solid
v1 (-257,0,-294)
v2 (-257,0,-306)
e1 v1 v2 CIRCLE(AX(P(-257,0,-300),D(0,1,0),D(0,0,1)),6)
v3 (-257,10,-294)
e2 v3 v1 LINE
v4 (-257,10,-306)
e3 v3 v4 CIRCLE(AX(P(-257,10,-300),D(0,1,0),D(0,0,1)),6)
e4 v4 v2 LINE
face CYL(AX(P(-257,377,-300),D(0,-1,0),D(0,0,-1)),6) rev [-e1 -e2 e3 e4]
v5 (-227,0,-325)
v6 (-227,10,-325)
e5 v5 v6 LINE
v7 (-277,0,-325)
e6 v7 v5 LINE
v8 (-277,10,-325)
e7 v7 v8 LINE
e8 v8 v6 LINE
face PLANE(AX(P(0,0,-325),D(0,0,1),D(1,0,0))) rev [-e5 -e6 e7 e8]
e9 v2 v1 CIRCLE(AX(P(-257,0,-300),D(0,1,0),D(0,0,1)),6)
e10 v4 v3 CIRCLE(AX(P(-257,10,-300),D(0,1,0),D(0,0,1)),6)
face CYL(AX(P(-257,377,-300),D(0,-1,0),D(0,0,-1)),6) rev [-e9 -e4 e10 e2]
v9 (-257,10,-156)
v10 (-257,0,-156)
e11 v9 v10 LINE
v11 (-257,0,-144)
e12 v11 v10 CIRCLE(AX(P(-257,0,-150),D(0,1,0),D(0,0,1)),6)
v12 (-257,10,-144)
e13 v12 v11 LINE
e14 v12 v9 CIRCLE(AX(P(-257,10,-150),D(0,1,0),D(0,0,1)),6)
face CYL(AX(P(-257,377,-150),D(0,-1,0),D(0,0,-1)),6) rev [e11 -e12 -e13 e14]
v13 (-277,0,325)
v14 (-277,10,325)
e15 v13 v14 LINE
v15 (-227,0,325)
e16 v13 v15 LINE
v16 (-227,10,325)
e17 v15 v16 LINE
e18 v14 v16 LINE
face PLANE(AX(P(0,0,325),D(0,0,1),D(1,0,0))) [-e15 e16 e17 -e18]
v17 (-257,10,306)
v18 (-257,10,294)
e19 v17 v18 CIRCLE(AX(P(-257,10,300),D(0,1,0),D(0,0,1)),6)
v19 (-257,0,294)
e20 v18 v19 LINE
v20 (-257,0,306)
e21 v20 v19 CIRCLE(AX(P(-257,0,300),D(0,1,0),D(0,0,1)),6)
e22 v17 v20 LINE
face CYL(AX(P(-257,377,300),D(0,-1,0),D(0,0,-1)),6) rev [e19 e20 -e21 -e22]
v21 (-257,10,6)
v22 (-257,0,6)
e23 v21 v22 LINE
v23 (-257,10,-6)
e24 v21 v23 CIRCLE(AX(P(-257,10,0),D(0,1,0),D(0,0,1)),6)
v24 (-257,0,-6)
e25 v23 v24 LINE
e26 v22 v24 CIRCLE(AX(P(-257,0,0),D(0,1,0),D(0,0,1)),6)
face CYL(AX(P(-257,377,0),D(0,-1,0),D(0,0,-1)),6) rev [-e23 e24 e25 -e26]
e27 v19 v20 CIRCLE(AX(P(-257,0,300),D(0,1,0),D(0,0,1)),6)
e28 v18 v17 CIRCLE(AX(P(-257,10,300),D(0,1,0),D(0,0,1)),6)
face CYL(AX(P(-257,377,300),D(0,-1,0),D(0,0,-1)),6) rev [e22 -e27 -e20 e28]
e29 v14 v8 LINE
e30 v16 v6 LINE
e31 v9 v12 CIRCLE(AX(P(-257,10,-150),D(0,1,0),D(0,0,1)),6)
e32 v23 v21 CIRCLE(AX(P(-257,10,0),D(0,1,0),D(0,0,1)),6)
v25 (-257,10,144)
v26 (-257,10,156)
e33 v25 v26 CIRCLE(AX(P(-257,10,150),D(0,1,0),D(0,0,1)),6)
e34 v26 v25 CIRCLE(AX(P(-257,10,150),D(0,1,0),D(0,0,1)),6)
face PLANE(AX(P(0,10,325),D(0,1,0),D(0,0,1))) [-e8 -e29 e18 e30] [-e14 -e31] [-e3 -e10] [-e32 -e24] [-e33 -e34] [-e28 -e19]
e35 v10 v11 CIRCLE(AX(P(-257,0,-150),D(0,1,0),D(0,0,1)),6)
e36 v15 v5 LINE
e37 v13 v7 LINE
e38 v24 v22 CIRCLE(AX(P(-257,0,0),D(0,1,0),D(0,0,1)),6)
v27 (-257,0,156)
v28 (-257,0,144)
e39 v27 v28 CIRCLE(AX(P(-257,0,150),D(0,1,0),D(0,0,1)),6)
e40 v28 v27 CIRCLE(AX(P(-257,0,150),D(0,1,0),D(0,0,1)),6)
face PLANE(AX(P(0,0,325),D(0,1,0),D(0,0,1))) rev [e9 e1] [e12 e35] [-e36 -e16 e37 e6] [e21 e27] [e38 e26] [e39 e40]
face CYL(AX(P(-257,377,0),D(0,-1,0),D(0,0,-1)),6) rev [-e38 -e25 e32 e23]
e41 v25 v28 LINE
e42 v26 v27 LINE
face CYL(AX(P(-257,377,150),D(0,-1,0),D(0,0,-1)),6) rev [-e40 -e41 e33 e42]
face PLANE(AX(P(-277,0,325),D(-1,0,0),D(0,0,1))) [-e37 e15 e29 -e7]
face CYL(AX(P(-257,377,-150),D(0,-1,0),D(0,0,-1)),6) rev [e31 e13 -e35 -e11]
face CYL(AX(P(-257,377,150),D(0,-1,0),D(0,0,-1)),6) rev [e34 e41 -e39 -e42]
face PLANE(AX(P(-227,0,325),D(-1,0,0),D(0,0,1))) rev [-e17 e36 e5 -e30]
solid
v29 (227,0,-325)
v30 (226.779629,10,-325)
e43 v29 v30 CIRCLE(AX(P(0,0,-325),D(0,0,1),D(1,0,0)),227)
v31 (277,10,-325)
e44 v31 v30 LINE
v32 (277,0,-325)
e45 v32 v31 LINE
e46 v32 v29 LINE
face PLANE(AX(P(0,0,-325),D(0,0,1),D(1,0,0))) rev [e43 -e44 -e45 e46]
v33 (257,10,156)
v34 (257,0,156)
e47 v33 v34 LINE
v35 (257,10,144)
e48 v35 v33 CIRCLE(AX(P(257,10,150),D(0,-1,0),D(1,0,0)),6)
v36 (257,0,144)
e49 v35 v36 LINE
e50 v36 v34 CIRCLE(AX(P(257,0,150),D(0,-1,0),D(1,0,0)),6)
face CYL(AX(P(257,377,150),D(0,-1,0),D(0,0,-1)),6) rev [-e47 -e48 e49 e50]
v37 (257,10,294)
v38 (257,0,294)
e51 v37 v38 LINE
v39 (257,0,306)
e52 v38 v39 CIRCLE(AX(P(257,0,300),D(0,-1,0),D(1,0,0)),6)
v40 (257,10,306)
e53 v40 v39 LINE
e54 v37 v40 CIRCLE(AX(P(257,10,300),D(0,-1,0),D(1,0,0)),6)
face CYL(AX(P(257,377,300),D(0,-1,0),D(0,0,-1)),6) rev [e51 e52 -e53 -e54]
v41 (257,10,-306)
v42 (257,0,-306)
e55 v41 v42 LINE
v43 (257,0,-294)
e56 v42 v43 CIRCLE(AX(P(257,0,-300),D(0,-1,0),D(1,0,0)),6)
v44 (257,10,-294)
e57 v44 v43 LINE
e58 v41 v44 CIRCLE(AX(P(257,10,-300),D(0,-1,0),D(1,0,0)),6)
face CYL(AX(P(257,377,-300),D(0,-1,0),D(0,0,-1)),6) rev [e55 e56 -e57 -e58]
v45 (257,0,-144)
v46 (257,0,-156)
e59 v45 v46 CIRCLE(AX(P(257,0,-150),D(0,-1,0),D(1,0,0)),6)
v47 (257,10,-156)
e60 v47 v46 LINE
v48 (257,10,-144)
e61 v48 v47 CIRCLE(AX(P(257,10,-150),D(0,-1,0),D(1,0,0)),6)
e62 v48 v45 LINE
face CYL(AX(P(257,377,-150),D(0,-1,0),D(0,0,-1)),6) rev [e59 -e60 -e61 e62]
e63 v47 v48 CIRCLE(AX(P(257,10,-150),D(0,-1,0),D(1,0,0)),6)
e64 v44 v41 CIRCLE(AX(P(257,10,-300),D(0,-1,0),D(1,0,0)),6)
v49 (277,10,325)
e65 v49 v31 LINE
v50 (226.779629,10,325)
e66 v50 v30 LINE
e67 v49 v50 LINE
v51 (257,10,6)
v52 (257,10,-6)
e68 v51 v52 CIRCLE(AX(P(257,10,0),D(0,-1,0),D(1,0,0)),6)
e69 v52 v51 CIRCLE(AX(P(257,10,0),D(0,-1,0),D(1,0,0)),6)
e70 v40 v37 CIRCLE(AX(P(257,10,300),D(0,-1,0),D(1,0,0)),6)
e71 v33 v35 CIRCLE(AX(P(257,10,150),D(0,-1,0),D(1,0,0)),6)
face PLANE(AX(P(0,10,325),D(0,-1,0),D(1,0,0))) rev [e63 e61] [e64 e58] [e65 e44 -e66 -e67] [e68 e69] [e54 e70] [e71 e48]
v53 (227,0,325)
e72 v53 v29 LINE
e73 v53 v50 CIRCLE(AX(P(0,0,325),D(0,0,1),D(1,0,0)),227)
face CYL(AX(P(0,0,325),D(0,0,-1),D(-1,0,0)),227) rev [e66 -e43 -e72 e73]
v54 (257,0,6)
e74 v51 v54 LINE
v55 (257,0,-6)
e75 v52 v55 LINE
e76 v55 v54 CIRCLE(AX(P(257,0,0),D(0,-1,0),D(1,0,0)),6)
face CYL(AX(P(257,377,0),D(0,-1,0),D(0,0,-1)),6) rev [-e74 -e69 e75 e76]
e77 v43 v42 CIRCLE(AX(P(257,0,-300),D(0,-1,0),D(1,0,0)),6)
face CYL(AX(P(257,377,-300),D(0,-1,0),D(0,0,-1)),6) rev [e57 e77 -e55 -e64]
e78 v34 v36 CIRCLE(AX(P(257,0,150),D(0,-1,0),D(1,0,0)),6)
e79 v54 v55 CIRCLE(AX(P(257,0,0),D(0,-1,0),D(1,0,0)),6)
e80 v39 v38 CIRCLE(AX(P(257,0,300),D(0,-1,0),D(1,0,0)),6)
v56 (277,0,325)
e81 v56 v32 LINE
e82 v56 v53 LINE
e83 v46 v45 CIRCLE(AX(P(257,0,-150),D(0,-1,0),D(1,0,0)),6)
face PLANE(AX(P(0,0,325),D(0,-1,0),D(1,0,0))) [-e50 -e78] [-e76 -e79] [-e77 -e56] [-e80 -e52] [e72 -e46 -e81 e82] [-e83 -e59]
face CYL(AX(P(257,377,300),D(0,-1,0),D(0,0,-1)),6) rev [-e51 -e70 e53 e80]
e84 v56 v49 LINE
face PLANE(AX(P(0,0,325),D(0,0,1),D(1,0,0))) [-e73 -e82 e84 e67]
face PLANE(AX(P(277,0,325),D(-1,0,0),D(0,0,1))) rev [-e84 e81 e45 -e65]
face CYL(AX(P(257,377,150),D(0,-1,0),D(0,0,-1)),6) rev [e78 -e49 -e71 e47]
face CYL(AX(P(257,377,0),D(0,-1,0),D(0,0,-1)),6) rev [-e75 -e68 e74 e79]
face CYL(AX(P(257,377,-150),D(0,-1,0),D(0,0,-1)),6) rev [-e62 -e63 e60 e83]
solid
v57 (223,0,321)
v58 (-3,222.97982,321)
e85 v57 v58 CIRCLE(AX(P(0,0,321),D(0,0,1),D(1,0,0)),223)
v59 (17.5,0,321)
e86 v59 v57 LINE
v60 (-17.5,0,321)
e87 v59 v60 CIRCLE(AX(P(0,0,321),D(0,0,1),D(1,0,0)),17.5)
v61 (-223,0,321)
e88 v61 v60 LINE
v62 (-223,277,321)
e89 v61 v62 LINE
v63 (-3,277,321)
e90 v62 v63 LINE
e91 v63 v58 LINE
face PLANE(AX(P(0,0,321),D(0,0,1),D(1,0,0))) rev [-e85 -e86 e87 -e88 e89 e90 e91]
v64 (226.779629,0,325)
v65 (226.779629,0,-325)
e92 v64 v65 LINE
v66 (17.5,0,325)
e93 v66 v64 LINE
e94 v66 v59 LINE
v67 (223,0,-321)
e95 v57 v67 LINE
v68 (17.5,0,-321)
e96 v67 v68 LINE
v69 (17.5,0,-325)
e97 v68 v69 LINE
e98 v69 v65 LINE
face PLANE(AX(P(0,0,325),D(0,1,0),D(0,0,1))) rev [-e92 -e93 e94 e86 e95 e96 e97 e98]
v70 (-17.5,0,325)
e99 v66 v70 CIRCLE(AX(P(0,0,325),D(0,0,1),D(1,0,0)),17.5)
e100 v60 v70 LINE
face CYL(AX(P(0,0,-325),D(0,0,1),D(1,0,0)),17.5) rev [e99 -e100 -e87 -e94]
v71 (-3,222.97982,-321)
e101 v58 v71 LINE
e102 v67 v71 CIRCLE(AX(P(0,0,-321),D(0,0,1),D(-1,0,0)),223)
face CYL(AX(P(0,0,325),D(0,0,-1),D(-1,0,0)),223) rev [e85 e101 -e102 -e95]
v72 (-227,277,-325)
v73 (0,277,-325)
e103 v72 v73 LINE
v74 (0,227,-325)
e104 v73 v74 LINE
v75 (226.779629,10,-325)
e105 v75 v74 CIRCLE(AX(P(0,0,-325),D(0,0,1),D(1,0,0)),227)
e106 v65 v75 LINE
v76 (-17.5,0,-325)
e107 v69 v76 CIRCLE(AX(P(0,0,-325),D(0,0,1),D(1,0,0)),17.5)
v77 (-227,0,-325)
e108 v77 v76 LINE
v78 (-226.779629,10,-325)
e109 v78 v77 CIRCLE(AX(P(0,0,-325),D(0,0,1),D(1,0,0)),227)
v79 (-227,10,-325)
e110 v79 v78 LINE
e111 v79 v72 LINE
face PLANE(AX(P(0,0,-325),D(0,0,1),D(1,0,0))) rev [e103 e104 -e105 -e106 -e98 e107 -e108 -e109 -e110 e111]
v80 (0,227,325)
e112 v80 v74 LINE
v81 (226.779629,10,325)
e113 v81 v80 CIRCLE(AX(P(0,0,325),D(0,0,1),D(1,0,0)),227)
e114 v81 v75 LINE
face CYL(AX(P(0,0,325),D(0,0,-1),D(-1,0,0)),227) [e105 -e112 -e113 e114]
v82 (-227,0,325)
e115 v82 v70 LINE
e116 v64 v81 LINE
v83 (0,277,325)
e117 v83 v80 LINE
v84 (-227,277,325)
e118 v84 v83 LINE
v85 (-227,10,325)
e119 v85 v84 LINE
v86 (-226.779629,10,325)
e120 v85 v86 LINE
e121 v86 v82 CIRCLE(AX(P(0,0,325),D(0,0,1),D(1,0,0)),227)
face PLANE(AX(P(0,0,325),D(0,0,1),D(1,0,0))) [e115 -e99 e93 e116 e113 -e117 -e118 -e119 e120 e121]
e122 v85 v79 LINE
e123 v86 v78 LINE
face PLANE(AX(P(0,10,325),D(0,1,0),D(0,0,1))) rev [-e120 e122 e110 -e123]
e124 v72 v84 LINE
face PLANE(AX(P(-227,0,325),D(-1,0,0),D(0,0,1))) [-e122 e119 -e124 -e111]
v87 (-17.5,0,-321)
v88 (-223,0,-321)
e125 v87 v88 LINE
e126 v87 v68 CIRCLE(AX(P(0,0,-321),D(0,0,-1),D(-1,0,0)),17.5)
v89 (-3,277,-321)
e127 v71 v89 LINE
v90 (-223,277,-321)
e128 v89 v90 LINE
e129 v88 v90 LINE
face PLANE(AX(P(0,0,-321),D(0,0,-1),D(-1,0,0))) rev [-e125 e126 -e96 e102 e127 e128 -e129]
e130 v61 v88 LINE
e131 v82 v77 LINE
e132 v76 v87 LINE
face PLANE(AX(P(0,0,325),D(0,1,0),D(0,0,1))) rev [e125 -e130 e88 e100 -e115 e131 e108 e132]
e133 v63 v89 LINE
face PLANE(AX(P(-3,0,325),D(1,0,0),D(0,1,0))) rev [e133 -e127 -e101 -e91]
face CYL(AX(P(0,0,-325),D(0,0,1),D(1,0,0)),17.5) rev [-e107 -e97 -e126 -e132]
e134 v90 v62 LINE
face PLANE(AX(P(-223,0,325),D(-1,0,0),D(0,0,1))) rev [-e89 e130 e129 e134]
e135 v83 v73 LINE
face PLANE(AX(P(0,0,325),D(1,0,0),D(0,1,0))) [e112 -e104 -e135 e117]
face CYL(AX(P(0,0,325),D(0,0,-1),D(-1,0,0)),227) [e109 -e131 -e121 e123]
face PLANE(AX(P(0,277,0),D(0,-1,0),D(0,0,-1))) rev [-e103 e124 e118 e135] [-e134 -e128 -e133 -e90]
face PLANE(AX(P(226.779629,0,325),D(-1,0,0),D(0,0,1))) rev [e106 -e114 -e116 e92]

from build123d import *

# Parameters (mm, degrees)
SKETCH1_W               = 50
SKETCH1_H               = 10
BOSS_EXTRUDE1_DEPTH     = 325
BOSS_EXTRUDE4_DEPTH     = 4
BOSS_EXTRUDE5_START     = -4
BOSS_EXTRUDE5_DEPTH     = 4
SKETCH6_R               = 6
CUT_EXTRUDE1_DEPTH      = 570.634093081
LPATTERN1_COUNT         = 3
LPATTERN1_PITCH         = 150
LPATTERN2_COUNT         = 3
LPATTERN2_PITCH         = 150
CUT_EXTRUDE2_DEPTH      = 801.848300242
CUT_EXTRUDE2_DEPTH_BACK = 801.848300242
SKETCH7_R               = 17.5
SKETCH8_W               = 720.760198568
SKETCH8_H               = 761.43709551
CUT_EXTRUDE3_DEPTH      = 100


with BuildPart() as part:
    # Sketch1 → Boss-Extrude1 (new, symmetric)
    with BuildSketch(Plane.XY):
        with Locations((-252, 5)):
            Rectangle(SKETCH1_W, SKETCH1_H)
        with BuildLine():
            ThreePointArc((-226.779628715, 10), (-226.944900492, 5.00121394), (-227, 0))
            Line((-227, 0), (-226.920690991, 0))
            Line((-226.920690991, 0), (-223, 0))
            Line((-223, 0), (-223, 10))
            Line((-223, 10), (-226.779628715, 10))
        make_face()
        with BuildLine():
            ThreePointArc((-223, 42.426406871), (-225.473494157, 26.281237274), (-226.779628715, 10))
            Line((-226.779628715, 10), (-223, 10))
            Line((-223, 10), (-223, 42.426406871))
        make_face()
        with BuildLine():
            Line((-227, 377), (-227, 10))
            Line((-227, 10), (-226.779628715, 10))
            ThreePointArc((-226.779628715, 10), (-225.473494157, 26.281237274), (-223, 42.426406871))
            Line((-223, 42.426406871), (-223, 377))
            Line((-223, 377), (-227, 377))
        make_face()
        with BuildLine():
            Line((-3, 377), (-3, 226.980175346))
            ThreePointArc((-3, 226.980175346), (-1.500032751, 226.995043782), (0, 227))
            Line((0, 227), (0, 377))
            Line((0, 377), (-3, 377))
        make_face()
        with BuildLine():
            Line((-3, 226.980175346), (-3, 222.979819715))
            ThreePointArc((-3, 222.979819715), (-1.500033937, 222.994954872), (0, 223))
            Line((0, 223), (0, 227))
            ThreePointArc((0, 227), (-1.500032751, 226.995043782), (-3, 226.980175346))
        make_face()
        with BuildLine():
            ThreePointArc((0, 223), (157.684812205, 157.684812205), (223, 0))
            Line((223, 0), (226.779628715, 0))
            Line((226.779628715, 0), (226.779628715, 10))
            ThreePointArc((226.779628715, 10), (156.937885802, 164.010670385), (0, 227))
            Line((0, 227), (0, 223))
        make_face()
        with BuildLine():
            Line((277, 10), (226.779628715, 10))
            ThreePointArc((226.779628715, 10), (226.944900492, 5.00121394), (227, 0))
            Line((227, 0), (277, 0))
            Line((277, 0), (277, 10))
        make_face()
    extrude(amount=BOSS_EXTRUDE1_DEPTH, both=True)

    # Sketch3 → Boss-Extrude4 (add)
    with BuildSketch(Plane.XY.offset(325)):
        with BuildLine():
            Line((-223, 0), (223, 0))
            ThreePointArc((223, 0), (156.620560592, 158.741928929), (-3, 222.979819715))
            Line((-3, 222.979819715), (-3, 377))
            Line((-3, 377), (-223, 377))
            Line((-223, 377), (-223, 0))
        make_face()
    extrude(amount=-BOSS_EXTRUDE4_DEPTH)

    # Sketch4 → Boss-Extrude5 (add)
    with BuildSketch(Plane(origin=(0, 0, -325), x_dir=(-1, 0, 0), z_dir=(0, 0, -1)).offset(BOSS_EXTRUDE5_START)):
        with BuildLine():
            Line((-223, 0), (223, 0))
            Line((223, 0), (223, 377))
            Line((223, 377), (3, 377))
            Line((3, 377), (3, 222.979819715))
            ThreePointArc((3, 222.979819715), (-156.620560592, 158.741928929), (-223, 0))
        make_face()
    extrude(amount=BOSS_EXTRUDE5_DEPTH)

    # Sketch6 → Cut-Extrude1 (cut, symmetric)
    with BuildSketch(Plane.XZ):
        with Locations((257, 0)):
            Circle(SKETCH6_R)
        with Locations(Location((-257, 0, 0), (0, 0, 90))):
            Circle(SKETCH6_R)
    cut_extrude1 = extrude(amount=CUT_EXTRUDE1_DEPTH, both=True, mode=Mode.SUBTRACT)

    # LPattern1: Cut-Extrude1 ×3
    with Locations(*[(0, 0, -i * LPATTERN1_PITCH) for i in range(1, LPATTERN1_COUNT)]):
        add(cut_extrude1, mode=Mode.SUBTRACT)

    # LPattern2: Cut-Extrude1 ×3
    with Locations(*[(0, 0, i * LPATTERN2_PITCH) for i in range(1, LPATTERN2_COUNT)]):
        add(cut_extrude1, mode=Mode.SUBTRACT)

    # Sketch7 → Cut-Extrude2 (cut, two sides: drawn at the far end of the back side and taken through both)
    with BuildSketch(Plane.XY.offset(325).offset(-CUT_EXTRUDE2_DEPTH_BACK)):
        Circle(SKETCH7_R)
    extrude(amount=CUT_EXTRUDE2_DEPTH + CUT_EXTRUDE2_DEPTH_BACK, mode=Mode.SUBTRACT)

    # Sketch8 → Cut-Extrude3 (cut)
    with BuildSketch(Plane(origin=(0, 377, 0), x_dir=(1, 0, 0), z_dir=(0, 1, 0))):
        with Locations((4.182407147, 0)):
            Rectangle(SKETCH8_W, SKETCH8_H)
    extrude(amount=-CUT_EXTRUDE3_DEPTH, mode=Mode.SUBTRACT)


solid = part.part
